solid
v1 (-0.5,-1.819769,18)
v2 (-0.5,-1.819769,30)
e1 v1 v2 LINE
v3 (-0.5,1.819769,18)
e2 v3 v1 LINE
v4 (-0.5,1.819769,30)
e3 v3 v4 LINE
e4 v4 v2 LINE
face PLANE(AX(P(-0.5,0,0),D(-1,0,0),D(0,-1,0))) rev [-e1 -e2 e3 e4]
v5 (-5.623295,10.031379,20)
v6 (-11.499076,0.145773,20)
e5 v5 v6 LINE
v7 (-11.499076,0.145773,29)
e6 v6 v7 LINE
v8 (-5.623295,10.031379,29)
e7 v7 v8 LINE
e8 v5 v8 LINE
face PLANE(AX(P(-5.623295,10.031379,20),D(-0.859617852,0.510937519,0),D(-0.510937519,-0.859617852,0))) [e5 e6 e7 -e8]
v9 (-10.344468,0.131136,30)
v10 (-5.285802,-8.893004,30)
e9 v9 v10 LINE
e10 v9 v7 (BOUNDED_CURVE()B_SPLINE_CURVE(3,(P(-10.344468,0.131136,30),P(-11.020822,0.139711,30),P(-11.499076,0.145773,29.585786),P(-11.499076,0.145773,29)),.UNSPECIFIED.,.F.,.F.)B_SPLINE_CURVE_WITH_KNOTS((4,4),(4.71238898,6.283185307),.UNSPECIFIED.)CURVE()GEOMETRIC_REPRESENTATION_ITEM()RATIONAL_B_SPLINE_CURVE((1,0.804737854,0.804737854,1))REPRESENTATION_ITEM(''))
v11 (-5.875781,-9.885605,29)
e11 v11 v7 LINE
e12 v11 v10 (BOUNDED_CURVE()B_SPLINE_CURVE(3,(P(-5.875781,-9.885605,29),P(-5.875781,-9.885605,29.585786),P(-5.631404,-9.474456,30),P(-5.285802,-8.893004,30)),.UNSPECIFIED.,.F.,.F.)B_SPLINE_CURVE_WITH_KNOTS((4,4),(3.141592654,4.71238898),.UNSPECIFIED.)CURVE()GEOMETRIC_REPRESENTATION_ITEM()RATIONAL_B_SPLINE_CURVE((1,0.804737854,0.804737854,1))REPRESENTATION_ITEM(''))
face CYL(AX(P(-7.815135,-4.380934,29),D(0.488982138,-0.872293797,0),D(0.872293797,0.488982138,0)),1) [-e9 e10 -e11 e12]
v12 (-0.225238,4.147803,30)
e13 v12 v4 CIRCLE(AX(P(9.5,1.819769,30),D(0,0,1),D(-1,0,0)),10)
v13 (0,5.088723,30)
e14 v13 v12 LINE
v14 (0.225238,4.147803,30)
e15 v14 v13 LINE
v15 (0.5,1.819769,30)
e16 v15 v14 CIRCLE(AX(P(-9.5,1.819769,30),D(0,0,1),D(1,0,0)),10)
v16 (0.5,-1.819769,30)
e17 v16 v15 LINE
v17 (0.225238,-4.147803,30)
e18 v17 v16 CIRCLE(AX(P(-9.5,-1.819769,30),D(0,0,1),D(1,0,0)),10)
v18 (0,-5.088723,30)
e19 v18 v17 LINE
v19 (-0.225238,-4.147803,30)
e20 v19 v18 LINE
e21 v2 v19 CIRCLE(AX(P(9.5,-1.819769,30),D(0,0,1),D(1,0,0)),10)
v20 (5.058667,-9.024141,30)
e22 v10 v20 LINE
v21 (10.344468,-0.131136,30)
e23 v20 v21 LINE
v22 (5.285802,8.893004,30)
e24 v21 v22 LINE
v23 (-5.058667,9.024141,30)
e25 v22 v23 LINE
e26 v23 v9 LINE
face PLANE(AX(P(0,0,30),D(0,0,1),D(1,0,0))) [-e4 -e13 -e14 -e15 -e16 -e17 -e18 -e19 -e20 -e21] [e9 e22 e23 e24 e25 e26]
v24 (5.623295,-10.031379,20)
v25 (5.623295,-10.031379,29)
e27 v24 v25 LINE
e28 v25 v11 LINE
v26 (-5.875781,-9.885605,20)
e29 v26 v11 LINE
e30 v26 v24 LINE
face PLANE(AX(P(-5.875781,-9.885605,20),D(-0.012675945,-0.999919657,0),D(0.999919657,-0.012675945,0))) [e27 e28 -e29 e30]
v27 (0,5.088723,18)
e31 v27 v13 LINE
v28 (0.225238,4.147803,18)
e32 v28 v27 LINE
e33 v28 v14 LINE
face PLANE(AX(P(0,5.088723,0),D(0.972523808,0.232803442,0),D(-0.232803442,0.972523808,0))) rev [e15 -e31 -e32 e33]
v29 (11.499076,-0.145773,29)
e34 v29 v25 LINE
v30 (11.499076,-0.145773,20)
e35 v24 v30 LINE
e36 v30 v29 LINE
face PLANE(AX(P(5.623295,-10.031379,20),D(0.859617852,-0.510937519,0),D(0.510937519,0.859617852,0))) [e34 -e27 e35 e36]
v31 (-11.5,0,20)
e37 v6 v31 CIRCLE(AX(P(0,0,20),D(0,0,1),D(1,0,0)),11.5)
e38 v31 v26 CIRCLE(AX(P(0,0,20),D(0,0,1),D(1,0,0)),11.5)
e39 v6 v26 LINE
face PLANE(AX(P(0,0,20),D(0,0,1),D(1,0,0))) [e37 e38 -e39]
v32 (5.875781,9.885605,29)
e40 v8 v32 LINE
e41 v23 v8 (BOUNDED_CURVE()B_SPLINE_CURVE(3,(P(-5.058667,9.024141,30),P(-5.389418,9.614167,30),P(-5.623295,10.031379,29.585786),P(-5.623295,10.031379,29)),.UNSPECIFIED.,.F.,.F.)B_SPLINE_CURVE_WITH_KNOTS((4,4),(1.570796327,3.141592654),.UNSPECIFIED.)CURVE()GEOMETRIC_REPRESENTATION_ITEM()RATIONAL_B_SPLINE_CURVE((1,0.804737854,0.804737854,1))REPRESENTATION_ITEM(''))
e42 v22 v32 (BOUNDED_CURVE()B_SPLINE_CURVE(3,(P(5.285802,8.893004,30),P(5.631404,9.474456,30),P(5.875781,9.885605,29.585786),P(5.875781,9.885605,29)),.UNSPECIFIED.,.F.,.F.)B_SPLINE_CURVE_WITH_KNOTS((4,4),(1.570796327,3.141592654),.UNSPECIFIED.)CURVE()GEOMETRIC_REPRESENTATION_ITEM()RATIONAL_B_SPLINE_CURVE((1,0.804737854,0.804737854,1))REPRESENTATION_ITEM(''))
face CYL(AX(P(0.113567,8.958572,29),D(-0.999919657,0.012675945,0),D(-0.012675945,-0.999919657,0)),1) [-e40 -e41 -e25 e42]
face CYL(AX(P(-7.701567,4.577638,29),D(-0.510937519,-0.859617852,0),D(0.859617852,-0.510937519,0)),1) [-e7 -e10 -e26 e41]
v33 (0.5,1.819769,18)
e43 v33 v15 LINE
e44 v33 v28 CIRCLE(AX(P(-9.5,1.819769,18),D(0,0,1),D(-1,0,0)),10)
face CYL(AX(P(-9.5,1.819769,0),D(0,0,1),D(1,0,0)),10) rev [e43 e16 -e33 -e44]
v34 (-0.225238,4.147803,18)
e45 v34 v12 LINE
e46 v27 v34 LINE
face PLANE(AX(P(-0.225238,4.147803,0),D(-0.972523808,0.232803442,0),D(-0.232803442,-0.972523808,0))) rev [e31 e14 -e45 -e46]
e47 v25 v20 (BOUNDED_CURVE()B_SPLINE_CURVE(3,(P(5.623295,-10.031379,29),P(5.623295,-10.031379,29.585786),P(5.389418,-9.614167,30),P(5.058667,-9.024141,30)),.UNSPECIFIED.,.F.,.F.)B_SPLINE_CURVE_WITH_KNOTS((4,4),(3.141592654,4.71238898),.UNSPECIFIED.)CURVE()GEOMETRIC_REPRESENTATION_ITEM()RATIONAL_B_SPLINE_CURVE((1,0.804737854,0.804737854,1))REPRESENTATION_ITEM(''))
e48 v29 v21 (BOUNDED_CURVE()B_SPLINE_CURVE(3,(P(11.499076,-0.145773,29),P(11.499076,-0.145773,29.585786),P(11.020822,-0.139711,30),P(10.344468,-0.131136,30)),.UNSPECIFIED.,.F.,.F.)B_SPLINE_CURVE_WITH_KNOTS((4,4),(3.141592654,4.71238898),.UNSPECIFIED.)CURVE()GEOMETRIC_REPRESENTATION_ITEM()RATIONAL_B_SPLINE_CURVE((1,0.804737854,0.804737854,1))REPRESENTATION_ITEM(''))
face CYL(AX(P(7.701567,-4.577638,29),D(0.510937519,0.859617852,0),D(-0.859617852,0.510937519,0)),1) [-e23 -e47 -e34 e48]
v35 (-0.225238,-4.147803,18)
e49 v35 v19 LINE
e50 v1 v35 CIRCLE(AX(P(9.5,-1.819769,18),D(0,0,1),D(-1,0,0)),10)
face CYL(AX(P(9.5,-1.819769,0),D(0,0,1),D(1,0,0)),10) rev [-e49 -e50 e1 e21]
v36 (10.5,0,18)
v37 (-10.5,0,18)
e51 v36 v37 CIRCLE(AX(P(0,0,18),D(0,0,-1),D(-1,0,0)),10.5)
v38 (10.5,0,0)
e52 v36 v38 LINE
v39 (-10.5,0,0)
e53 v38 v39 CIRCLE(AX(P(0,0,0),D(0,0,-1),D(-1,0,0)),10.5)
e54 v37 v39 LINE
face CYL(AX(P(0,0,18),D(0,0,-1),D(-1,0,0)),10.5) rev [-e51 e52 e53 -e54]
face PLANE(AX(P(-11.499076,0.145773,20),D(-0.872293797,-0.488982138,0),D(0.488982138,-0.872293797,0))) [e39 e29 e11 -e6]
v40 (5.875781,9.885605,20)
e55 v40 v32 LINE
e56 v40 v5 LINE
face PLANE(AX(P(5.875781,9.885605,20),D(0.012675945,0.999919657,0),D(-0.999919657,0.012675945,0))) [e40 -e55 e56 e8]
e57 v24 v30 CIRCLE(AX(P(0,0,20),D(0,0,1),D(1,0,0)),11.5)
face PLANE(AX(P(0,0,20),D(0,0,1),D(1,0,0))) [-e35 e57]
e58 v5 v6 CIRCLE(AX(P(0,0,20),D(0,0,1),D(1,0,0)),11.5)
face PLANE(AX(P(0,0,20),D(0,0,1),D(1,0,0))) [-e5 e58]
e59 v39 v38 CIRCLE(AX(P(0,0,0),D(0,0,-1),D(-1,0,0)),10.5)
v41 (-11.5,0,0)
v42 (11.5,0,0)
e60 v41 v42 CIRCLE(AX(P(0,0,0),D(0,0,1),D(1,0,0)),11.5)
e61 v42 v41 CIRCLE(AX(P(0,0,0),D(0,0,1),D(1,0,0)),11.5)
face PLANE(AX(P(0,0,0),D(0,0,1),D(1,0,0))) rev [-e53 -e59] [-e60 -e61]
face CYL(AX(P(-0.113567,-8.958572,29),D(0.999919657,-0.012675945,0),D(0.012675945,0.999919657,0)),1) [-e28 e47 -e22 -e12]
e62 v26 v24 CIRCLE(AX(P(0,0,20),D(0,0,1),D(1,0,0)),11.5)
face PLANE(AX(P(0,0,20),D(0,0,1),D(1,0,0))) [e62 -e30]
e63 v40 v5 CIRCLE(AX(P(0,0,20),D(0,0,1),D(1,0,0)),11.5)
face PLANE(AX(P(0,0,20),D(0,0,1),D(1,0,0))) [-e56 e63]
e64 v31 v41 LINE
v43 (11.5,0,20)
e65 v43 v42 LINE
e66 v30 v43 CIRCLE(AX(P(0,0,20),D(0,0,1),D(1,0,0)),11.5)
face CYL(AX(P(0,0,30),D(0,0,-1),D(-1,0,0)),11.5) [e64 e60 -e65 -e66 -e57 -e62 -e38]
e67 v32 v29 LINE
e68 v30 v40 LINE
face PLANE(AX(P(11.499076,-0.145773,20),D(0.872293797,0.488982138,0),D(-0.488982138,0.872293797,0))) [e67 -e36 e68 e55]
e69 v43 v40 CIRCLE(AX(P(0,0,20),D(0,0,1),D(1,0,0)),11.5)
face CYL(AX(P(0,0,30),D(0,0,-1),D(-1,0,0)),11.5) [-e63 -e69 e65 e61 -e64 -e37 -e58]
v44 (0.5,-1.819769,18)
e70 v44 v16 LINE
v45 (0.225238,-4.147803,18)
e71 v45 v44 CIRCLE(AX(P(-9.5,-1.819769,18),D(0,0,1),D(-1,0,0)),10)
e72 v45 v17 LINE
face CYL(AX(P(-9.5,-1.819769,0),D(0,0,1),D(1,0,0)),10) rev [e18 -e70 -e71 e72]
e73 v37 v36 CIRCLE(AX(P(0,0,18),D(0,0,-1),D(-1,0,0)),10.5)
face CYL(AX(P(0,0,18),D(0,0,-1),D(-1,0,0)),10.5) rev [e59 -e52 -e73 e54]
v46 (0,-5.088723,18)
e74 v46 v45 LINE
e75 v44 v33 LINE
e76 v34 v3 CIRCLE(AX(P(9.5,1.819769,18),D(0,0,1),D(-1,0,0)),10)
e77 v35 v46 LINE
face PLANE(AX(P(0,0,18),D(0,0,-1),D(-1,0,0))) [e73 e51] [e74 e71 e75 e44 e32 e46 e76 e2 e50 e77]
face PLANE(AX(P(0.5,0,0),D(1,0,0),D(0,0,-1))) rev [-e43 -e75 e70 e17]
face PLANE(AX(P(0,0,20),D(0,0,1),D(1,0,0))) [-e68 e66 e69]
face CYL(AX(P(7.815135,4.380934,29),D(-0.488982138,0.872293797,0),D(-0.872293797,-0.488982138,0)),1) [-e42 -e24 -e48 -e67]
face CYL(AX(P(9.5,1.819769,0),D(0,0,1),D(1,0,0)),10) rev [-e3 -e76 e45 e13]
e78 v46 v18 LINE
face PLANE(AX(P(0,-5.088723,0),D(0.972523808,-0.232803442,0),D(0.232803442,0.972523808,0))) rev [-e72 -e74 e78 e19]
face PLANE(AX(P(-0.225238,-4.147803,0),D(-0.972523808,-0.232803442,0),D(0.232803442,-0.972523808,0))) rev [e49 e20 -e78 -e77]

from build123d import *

# Parameters (mm, degrees)
SKETCH1_R           = 11.5
BOSS_EXTRUDE1_DEPTH = 30
SKETCH2_OUTSIDE_W   = 33.85
SKETCH2_OUTSIDE_H   = 33.85
CUT_EXTRUDE2_DEPTH  = 10
FILLET1_R           = 1
CUT_EXTRUDE3_DEPTH  = 35.124771062
SKETCH4_R           = 10.5
CUT_EXTRUDE4_DEPTH  = 18


with BuildPart() as part:
    # Sketch1 → Boss-Extrude1 (new body)
    with BuildSketch(Plane.XY):
        Circle(SKETCH1_R)
    extrude(amount=BOSS_EXTRUDE1_DEPTH)

    # Sketch2 outside → Cut-Extrude2 (cut)
    with BuildSketch(Plane.XY.offset(30)):
        Rectangle(SKETCH2_OUTSIDE_W, SKETCH2_OUTSIDE_H)
        Polygon((5.875781464, 9.885605302), (-5.623294591, 10.031378666), (-11.499076055, 0.145773364), (-5.875781464, -9.885605302), (5.623294591, -10.031378666), (11.499076055, -0.145773364), align=None, mode=Mode.SUBTRACT)
    extrude(amount=-CUT_EXTRUDE2_DEPTH, mode=Mode.SUBTRACT)

    # Fillet1
    fillet1_edges = [part.edges().sort_by_distance(p)[0] for p in [
        (8.68742876, 4.869915969, 30),
        (8.561185323, -5.088576015, 30),
        (-0.126243437, -9.958491984, 30),
        (-8.68742876, -4.869915969, 30),
        (-8.561185323, 5.088576015, 30),
        (0.126243437, 9.958491984, 30),
    ]]
    fillet(fillet1_edges, radius=FILLET1_R)

    # Sketch3 → Cut-Extrude3 (cut, through all)
    with BuildSketch(Plane.XY.offset(30)):
        with BuildLine():
            Line((0.5, 0), (0.5, 1.81976866))
            ThreePointArc((0.5, 1.81976866), (0.431071967, 2.991864898), (0.225238082, 4.147803077))
            Line((0.225238082, 4.147803077), (0, 5.088723004))
            Line((0, 5.088723004), (-0.225238082, 4.147803077))
            ThreePointArc((-0.225238082, 4.147803077), (-0.431071967, 2.991864898), (-0.5, 1.81976866))
            Line((-0.5, 1.81976866), (-0.5, 0))
            Line((-0.5, 0), (-0.5, -1.81976866))
            ThreePointArc((-0.5, -1.81976866), (-0.431071967, -2.991864898), (-0.225238082, -4.147803077))
            Line((-0.225238082, -4.147803077), (0, -5.088723004))
            Line((0, -5.088723004), (0.225238082, -4.147803077))
            ThreePointArc((0.225238082, -4.147803077), (0.431071967, -2.991864898), (0.5, -1.81976866))
            Line((0.5, -1.81976866), (0.5, 0))
        make_face()
    extrude(amount=-CUT_EXTRUDE3_DEPTH, mode=Mode.SUBTRACT)

    # Sketch4 → Cut-Extrude4 (cut)
    with BuildSketch(Plane(origin=(0, 0, 0), x_dir=(-1, 0, 0), z_dir=(0, 0, -1))):
        Circle(SKETCH4_R)
    extrude(amount=-CUT_EXTRUDE4_DEPTH, mode=Mode.SUBTRACT)


solid = part.part
